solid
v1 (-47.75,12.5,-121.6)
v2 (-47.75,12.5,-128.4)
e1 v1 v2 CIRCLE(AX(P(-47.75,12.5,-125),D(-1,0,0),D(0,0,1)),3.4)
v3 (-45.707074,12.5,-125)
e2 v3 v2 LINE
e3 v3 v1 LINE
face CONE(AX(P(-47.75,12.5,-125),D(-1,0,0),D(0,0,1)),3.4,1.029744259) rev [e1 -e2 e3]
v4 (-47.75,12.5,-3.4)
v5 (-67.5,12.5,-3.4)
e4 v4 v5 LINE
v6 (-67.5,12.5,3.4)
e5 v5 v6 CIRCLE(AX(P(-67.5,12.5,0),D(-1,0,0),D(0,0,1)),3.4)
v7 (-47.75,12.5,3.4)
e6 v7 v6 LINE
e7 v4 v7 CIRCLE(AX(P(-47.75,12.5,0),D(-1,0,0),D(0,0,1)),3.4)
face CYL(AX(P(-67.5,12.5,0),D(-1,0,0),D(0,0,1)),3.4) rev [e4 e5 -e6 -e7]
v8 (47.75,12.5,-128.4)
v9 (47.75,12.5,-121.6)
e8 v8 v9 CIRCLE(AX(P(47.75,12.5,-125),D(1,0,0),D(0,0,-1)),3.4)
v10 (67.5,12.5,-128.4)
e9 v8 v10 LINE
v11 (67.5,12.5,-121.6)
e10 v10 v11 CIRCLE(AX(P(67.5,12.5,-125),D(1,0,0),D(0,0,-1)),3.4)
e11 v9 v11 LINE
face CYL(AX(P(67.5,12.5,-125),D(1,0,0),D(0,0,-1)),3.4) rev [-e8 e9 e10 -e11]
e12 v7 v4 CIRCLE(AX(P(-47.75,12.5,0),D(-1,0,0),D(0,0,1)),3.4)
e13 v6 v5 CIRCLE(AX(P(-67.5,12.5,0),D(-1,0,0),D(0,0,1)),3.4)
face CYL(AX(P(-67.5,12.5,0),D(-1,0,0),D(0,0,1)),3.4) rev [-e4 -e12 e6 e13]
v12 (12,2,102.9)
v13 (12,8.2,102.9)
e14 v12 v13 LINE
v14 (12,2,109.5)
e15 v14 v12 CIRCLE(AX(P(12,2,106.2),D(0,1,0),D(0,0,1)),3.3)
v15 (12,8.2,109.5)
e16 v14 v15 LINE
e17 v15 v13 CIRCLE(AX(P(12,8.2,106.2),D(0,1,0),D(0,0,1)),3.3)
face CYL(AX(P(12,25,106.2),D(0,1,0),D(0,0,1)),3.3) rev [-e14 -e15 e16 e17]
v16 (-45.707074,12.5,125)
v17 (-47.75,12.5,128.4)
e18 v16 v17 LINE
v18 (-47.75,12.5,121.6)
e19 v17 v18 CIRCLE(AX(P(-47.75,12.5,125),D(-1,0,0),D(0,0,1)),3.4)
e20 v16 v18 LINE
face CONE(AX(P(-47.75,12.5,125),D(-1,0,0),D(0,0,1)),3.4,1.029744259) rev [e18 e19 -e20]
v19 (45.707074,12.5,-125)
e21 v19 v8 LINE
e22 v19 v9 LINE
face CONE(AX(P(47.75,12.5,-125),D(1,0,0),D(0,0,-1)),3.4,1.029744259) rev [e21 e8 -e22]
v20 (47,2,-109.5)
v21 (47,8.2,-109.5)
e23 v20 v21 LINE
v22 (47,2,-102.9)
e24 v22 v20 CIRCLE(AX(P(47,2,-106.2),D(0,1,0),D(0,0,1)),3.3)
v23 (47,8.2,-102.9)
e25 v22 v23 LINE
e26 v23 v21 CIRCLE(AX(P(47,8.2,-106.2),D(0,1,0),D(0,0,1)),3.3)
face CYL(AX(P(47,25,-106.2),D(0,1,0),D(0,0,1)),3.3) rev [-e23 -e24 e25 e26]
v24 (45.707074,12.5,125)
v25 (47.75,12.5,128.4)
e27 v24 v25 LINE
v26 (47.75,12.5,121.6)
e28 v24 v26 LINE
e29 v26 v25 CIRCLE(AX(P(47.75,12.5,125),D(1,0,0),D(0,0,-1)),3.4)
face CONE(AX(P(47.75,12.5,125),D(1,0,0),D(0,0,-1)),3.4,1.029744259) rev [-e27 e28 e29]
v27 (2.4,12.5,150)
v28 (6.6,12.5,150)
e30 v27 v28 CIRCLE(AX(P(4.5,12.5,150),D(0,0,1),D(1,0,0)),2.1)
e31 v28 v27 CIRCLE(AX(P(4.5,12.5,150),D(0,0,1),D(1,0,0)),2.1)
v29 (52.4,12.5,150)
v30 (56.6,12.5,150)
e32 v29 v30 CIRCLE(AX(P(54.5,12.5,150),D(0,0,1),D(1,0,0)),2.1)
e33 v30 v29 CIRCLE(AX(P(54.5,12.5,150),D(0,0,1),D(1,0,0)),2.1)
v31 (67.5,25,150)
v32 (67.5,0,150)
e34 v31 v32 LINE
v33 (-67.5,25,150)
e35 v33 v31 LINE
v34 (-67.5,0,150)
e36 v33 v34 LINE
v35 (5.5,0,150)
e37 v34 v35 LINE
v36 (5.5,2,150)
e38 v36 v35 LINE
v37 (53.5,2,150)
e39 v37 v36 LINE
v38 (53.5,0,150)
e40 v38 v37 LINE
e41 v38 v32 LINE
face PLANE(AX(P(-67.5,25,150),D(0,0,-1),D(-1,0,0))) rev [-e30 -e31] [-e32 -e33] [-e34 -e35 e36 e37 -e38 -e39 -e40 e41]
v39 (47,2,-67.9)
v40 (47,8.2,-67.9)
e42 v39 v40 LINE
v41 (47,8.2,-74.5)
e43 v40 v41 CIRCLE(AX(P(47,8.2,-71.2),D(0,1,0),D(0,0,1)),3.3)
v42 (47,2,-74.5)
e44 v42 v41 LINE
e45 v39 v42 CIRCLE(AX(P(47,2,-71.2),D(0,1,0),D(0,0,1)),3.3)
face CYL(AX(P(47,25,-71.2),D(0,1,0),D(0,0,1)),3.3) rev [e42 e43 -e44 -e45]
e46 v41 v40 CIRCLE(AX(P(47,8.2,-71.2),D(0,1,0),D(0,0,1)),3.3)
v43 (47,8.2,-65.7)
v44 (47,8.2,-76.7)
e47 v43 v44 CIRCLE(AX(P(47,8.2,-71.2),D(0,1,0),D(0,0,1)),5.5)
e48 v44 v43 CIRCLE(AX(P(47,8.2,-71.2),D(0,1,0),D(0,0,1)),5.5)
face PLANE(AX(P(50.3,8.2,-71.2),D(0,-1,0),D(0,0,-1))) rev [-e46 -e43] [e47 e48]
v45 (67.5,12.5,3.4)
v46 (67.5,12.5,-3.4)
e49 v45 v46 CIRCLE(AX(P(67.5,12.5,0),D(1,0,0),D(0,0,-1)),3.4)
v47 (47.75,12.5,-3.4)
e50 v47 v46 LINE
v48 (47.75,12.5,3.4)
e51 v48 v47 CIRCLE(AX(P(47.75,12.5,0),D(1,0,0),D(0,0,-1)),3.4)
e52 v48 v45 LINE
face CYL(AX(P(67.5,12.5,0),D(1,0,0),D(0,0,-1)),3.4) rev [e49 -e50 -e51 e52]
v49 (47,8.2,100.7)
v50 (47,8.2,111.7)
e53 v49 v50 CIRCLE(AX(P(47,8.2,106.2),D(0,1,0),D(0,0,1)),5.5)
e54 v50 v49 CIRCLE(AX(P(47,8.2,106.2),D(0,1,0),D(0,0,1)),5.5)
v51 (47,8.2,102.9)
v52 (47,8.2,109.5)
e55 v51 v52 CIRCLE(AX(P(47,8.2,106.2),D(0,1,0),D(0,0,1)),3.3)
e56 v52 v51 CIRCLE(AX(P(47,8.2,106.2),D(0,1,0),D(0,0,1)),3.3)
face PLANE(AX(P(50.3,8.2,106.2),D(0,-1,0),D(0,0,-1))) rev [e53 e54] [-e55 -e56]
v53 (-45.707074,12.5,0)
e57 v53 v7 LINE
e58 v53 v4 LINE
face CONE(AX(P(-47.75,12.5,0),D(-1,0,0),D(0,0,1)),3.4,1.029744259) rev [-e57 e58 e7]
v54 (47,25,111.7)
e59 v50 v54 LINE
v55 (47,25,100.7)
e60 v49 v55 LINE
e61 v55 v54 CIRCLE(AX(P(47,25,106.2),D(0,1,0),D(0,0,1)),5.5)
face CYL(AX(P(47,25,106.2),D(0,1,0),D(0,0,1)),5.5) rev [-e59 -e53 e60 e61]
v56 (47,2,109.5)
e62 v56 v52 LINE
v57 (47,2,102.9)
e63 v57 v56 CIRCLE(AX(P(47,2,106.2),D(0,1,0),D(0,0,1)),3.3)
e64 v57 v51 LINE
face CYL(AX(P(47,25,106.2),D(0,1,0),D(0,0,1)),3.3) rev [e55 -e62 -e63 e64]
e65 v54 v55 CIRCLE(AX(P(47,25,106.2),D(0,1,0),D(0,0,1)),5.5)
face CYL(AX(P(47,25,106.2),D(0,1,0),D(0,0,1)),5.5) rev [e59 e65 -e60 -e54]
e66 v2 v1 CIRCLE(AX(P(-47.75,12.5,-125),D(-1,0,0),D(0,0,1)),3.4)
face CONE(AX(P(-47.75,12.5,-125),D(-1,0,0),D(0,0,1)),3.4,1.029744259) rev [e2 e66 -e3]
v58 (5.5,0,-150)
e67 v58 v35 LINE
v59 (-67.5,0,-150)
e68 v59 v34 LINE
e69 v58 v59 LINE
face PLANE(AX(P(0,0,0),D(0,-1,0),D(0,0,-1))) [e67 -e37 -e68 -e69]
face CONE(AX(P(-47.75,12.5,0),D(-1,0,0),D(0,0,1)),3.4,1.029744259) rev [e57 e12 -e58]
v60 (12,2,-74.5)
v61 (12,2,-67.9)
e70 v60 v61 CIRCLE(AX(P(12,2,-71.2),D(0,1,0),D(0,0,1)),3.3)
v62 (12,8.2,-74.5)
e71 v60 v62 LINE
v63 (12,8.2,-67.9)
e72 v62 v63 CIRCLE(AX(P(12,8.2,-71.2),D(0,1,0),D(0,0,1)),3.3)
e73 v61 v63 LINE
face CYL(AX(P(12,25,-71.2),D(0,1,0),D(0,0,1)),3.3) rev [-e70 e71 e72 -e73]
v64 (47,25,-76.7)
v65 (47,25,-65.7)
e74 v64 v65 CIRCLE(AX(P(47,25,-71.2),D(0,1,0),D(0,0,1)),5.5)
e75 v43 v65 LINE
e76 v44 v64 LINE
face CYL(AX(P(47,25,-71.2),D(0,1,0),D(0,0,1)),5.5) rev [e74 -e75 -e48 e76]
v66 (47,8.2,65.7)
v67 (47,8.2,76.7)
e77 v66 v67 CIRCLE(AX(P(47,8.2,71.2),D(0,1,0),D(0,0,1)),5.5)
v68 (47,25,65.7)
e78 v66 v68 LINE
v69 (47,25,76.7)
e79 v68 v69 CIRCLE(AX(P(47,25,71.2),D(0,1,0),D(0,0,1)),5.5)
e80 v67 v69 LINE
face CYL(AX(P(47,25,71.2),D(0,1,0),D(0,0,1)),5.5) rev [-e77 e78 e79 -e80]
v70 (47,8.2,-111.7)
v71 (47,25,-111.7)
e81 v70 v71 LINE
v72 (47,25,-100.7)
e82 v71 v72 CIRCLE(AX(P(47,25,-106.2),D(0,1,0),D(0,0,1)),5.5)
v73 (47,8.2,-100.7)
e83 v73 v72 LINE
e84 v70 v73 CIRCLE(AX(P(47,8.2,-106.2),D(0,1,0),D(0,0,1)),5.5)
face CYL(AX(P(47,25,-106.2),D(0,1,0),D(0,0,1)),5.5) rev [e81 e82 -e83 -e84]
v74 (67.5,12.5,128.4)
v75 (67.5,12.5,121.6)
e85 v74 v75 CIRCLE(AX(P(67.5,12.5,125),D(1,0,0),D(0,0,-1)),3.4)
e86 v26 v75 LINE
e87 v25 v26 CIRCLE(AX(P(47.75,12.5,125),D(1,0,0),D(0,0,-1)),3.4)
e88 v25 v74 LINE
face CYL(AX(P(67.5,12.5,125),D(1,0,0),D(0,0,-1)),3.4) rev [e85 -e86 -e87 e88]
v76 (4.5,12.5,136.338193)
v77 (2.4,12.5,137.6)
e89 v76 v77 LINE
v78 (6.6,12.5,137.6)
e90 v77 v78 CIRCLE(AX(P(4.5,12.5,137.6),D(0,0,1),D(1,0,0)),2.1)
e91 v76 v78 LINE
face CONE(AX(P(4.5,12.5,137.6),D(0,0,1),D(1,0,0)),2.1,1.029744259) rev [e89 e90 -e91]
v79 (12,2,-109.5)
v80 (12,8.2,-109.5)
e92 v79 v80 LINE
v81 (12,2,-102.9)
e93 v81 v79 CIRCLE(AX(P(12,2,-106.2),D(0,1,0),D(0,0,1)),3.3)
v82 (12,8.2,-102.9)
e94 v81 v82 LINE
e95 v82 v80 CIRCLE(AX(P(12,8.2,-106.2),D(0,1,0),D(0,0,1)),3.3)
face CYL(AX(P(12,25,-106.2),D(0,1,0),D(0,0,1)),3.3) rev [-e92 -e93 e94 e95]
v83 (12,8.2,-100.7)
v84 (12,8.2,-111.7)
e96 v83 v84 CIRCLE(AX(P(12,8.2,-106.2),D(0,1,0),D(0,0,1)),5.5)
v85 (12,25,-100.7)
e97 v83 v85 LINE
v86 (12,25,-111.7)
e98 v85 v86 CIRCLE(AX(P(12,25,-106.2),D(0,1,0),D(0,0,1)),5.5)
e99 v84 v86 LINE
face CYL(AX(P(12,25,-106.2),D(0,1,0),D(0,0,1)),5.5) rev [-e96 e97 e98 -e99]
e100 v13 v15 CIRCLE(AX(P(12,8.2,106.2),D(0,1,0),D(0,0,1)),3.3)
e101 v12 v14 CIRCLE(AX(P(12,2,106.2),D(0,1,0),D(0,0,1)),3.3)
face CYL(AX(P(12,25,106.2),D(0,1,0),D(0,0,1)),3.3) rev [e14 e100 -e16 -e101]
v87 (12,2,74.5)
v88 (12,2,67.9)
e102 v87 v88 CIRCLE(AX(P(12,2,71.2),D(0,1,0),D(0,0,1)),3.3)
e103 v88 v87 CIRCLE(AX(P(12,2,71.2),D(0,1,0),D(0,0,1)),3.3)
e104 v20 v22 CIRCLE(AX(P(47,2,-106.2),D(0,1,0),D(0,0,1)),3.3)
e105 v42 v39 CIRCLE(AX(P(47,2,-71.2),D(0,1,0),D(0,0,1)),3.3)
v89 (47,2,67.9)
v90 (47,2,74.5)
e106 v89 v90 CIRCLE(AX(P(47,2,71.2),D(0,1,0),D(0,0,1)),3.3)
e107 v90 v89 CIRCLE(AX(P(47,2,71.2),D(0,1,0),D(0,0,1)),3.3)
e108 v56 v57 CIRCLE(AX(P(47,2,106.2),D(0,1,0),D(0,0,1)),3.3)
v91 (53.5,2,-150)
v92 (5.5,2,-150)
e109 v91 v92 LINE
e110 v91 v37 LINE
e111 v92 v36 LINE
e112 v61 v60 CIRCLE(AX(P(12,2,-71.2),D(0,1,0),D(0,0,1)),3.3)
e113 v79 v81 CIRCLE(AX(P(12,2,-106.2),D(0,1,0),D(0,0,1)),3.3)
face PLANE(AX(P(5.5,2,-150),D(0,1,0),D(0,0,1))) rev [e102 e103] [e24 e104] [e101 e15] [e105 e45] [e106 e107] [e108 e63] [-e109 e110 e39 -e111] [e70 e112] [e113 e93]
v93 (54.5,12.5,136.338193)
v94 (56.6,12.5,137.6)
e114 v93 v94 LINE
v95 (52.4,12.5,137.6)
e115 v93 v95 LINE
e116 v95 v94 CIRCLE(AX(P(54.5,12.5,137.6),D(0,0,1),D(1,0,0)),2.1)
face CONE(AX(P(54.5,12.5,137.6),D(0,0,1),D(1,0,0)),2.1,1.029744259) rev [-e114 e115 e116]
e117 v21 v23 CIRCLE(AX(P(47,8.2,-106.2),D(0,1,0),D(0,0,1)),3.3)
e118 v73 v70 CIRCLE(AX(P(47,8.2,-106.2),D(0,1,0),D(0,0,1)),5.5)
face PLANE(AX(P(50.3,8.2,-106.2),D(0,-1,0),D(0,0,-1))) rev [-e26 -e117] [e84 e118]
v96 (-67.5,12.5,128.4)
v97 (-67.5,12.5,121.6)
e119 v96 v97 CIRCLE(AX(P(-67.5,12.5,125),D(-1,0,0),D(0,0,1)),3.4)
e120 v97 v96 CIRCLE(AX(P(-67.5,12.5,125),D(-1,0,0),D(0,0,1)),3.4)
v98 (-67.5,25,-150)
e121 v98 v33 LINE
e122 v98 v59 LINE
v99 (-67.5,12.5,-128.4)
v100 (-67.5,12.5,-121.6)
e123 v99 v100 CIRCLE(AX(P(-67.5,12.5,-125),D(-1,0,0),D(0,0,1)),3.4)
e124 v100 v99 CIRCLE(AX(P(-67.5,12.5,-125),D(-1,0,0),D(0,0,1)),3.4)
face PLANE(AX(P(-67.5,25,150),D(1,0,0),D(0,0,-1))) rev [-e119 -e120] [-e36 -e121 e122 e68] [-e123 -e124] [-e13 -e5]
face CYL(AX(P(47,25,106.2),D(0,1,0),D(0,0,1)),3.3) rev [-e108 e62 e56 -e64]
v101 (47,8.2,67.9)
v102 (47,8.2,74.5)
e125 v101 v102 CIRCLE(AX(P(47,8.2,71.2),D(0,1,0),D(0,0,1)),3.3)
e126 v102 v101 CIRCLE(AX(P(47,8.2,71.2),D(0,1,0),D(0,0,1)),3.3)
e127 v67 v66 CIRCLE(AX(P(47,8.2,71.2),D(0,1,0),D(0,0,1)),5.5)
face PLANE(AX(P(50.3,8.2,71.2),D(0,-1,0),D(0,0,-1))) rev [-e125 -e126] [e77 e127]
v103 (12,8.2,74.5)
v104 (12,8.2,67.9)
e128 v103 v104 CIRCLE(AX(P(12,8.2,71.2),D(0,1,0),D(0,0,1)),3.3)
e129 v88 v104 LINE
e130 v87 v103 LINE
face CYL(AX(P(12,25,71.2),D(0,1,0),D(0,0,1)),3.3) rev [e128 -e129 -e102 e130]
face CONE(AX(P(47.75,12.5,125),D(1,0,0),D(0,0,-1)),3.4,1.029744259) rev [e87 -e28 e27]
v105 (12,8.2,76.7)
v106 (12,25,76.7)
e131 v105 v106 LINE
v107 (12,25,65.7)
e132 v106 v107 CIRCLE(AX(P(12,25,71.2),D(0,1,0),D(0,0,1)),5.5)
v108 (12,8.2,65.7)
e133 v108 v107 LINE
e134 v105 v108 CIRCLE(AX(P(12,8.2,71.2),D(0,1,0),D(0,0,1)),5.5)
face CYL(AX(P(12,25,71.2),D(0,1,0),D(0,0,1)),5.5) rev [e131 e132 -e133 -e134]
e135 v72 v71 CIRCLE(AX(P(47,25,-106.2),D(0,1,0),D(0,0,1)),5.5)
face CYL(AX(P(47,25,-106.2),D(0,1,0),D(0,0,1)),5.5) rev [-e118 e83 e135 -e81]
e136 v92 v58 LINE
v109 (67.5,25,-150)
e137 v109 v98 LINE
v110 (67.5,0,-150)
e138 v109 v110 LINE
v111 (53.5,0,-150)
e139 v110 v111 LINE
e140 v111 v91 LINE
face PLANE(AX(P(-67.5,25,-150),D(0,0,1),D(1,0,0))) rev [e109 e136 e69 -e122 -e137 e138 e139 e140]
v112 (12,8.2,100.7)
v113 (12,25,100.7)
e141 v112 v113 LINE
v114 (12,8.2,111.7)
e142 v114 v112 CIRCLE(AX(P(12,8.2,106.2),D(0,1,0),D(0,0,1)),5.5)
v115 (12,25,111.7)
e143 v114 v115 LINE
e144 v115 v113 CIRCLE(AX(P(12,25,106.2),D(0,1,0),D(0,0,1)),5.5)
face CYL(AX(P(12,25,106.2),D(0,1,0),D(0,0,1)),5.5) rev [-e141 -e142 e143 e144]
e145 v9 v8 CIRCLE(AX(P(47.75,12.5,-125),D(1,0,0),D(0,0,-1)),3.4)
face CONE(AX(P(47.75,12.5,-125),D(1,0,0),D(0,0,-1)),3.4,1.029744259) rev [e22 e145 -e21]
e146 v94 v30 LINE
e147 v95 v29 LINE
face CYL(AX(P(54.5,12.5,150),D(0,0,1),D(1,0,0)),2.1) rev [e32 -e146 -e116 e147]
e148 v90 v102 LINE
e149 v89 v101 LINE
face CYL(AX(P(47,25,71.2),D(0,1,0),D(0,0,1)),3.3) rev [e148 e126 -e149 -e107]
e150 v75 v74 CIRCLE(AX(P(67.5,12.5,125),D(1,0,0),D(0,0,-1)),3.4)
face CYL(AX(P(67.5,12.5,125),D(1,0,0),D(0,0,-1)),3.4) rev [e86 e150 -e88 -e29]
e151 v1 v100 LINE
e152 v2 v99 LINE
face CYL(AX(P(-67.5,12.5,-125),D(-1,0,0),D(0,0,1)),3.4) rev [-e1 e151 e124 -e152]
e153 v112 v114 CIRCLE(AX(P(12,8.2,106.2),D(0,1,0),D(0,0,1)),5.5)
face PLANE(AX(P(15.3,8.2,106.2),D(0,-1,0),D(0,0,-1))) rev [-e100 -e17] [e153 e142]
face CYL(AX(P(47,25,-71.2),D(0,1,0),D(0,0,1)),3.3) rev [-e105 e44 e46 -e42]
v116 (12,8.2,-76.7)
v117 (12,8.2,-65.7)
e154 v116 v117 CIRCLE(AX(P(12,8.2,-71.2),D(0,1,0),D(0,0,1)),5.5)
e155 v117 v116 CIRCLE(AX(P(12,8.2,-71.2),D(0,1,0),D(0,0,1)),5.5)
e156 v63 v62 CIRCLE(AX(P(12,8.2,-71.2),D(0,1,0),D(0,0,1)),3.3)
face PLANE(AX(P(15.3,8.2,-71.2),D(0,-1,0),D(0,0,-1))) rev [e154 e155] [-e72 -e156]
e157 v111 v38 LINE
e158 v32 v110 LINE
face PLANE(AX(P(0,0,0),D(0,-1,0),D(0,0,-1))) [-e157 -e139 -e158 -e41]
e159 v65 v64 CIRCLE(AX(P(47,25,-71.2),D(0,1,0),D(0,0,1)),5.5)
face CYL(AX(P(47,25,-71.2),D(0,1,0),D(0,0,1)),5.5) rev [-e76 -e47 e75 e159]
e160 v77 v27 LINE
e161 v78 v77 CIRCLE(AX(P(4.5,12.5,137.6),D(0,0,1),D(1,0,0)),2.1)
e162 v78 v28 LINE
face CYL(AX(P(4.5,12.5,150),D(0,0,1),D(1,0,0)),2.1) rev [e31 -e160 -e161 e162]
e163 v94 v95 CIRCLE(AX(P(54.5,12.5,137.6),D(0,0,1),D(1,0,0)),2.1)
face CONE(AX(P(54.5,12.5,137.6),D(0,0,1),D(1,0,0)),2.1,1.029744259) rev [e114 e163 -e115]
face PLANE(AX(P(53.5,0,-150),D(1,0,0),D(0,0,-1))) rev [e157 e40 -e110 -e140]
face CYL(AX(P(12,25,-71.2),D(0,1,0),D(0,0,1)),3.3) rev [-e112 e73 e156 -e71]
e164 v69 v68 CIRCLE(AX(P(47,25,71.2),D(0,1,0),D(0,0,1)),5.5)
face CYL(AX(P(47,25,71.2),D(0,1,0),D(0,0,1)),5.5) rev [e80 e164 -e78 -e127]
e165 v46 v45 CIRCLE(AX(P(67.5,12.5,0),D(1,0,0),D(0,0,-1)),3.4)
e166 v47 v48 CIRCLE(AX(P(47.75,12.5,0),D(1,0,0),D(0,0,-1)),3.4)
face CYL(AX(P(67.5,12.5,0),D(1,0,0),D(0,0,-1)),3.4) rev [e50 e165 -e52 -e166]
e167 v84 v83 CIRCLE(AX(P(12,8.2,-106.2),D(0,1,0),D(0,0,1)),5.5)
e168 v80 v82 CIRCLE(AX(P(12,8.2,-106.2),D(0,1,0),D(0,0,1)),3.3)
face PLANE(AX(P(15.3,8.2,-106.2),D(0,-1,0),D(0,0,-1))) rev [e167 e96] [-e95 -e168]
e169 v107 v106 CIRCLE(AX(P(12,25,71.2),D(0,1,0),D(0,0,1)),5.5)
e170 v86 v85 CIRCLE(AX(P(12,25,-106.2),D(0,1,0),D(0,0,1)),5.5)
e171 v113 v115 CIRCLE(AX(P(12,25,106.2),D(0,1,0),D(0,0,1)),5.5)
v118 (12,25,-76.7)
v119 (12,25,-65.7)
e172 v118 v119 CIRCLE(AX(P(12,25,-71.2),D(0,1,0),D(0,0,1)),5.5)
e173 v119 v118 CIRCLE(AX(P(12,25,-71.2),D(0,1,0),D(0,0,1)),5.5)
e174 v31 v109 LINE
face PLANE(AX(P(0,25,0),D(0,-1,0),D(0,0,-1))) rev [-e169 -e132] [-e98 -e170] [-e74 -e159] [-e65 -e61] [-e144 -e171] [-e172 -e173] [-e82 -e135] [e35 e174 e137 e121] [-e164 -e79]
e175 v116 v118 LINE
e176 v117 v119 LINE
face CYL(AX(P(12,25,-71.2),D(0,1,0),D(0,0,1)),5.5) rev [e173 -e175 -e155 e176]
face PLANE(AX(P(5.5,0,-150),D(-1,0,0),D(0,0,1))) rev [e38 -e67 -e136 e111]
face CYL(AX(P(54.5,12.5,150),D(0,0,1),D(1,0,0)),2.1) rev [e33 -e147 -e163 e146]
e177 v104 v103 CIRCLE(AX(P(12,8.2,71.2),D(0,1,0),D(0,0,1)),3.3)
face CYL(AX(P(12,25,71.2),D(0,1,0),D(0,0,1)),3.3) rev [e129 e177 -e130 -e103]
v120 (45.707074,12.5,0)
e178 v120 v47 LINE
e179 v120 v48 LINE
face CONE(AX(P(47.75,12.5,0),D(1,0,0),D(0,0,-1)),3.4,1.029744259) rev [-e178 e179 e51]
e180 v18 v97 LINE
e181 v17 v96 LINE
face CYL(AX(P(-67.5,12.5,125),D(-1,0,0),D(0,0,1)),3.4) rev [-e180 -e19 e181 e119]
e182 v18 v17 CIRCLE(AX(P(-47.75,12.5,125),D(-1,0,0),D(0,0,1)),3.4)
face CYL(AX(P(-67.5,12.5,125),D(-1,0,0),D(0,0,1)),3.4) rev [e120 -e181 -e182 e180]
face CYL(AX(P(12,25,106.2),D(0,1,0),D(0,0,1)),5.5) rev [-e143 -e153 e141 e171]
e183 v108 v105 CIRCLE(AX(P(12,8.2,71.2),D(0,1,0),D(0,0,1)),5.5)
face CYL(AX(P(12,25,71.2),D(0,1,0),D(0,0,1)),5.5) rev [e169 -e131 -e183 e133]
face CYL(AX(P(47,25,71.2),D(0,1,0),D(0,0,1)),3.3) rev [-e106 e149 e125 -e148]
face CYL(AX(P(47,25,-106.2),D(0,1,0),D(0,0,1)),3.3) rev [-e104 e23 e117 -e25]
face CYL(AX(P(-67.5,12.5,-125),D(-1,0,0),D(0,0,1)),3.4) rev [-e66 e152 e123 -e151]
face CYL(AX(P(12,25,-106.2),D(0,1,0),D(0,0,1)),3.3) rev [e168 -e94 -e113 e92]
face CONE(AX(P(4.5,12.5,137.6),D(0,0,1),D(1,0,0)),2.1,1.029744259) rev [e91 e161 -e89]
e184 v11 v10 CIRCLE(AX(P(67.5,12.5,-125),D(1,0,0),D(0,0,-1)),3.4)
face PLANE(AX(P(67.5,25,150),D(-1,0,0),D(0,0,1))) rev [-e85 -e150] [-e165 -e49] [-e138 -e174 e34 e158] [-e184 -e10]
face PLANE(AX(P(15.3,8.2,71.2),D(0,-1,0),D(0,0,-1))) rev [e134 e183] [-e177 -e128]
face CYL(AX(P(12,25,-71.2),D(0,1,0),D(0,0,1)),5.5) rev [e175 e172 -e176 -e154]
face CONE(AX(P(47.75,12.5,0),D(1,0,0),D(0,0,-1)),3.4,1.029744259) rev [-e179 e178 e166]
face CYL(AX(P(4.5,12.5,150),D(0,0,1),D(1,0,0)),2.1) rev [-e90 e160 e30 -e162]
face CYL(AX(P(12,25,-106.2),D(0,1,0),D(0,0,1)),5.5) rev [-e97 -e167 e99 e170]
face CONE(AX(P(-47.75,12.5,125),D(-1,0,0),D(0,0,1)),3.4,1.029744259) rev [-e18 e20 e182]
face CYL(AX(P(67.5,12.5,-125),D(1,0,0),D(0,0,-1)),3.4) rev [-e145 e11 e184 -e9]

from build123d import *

# Parameters (mm, degrees)
SKETCH_1_W                   = 135
SKETCH_1_H                   = 300
EXTRUDE_1_DEPTH              = 25
SKETCH_2_W                   = 48
SKETCH_2_H                   = 2
CUT_EXTRUDE_1_DEPTH          = 309.514586365
HOLE_WIZARD_M8_1_AT_2_COUNT  = 2
HOLE_WIZARD_M8_1_AT_2_PITCH  = 250
HOLE_WIZARD_M8_1_AT_3_COUNT  = 2
HOLE_WIZARD_M8_1_AT_3_PITCH  = 125
HOLE_WIZARD_M6_1_D           = 6.6
HOLE_WIZARD_M6_1_CBORE_D     = 11
HOLE_WIZARD_M6_1_CBORE_DEPTH = 16.8
HOLE_WIZARD_M5_1_D           = 4.2
HOLE_WIZARD_M5_1_DEPTH       = 12.4
HOLE_WIZARD_M5_1_TIP         = 1.2618073


with BuildPart() as part:
    # 草图1 → 凸台-拉伸1 (new body)
    with BuildSketch(Plane(origin=(0, 0, 0), x_dir=(1, 0, 0), z_dir=(0, 1, 0))):
        Rectangle(SKETCH_1_W, SKETCH_1_H)
    extrude(amount=EXTRUDE_1_DEPTH)

    # 草图2 → 切除-拉伸1 (cut, through all)
    with BuildSketch(Plane.XY.offset(150)):
        with Locations((29.5, 1)):
            Rectangle(SKETCH_2_W, SKETCH_2_H)
    extrude(amount=-CUT_EXTRUDE_1_DEPTH, mode=Mode.SUBTRACT)

    # 草图6 → M8 螺纹孔1 (revolve, cut)
    with BuildSketch(Plane(origin=(-67.5, 12.5, -125), x_dir=(0, 0, 1), z_dir=(0, 1, 0))):
        Polygon((0, 0), (0, 21.792926105), (3.4, 19.75), (3.4, 0), align=None)
    hole_wizard_m8_1 = revolve(axis=Axis((-73.85, 12.5, -125), (1, 0, 0)), mode=Mode.SUBTRACT)

    # M8 螺纹孔1 at 2: M8 螺纹孔1 ×2
    with Locations(*[(0, 0, i * HOLE_WIZARD_M8_1_AT_2_PITCH) for i in range(1, HOLE_WIZARD_M8_1_AT_2_COUNT)]):
        add(hole_wizard_m8_1, mode=Mode.SUBTRACT)

    # M8 螺纹孔1 at 3: M8 螺纹孔1 ×2
    with Locations(*[(0, 0, i * HOLE_WIZARD_M8_1_AT_3_PITCH) for i in range(1, HOLE_WIZARD_M8_1_AT_3_COUNT)]):
        add(hole_wizard_m8_1, mode=Mode.SUBTRACT)

    # 镜向1: M8 螺纹孔1 across plane
    add(hole_wizard_m8_1.mirror(Plane(origin=(0, 0, 0), x_dir=(0, 0, 1), z_dir=(1, 0, 0))), mode=Mode.SUBTRACT)

    # 镜向1 copy 1 sketch → 镜向1 copy 1 (revolve, cut)
    with BuildSketch(Plane(origin=(67.5, 12.5, 125), x_dir=(0, 0, 1), z_dir=(0, 1, 0))):
        Polygon((0, 0), (0, -21.792926105), (3.4, -19.75), (3.4, 0), align=None)
    revolve(axis=Axis((73.85, 12.5, 125), (1, 0, 0)), mode=Mode.SUBTRACT)

    # 镜向1 copy 2 sketch → 镜向1 copy 2 (revolve, cut)
    with BuildSketch(Plane(origin=(67.5, 12.5, 0), x_dir=(0, 0, 1), z_dir=(0, 1, 0))):
        Polygon((0, 0), (0, -21.792926105), (3.4, -19.75), (3.4, 0), align=None)
    revolve(axis=Axis((73.85, 12.5, 0), (1, 0, 0)), mode=Mode.SUBTRACT)

    # M6 六角圆柱头螺钉的柱形沉头孔1 (through all)
    with Locations(Plane(origin=(0, 25, 0), x_dir=(1, 0, 0), z_dir=(0, 1, 0))):
        with Locations((12, -71.2), (47, -71.2), (47, -106.2), (12, -106.2), (12, 71.2), (12, 106.2), (47, 106.2), (47, 71.2)):
            CounterBoreHole(HOLE_WIZARD_M6_1_D / 2, HOLE_WIZARD_M6_1_CBORE_D / 2, HOLE_WIZARD_M6_1_CBORE_DEPTH)

    # M5 螺纹孔1
    with Locations(Plane.XY.offset(150)):
        with Locations((4.5, 12.5), (54.5, 12.5)):
            Hole(HOLE_WIZARD_M5_1_D / 2, depth=HOLE_WIZARD_M5_1_DEPTH)
            with Locations((0, 0, -(HOLE_WIZARD_M5_1_DEPTH + HOLE_WIZARD_M5_1_TIP / 2))):  # 118° drill point
                Cone(0, HOLE_WIZARD_M5_1_D / 2, HOLE_WIZARD_M5_1_TIP, mode=Mode.SUBTRACT)


solid = part.part
